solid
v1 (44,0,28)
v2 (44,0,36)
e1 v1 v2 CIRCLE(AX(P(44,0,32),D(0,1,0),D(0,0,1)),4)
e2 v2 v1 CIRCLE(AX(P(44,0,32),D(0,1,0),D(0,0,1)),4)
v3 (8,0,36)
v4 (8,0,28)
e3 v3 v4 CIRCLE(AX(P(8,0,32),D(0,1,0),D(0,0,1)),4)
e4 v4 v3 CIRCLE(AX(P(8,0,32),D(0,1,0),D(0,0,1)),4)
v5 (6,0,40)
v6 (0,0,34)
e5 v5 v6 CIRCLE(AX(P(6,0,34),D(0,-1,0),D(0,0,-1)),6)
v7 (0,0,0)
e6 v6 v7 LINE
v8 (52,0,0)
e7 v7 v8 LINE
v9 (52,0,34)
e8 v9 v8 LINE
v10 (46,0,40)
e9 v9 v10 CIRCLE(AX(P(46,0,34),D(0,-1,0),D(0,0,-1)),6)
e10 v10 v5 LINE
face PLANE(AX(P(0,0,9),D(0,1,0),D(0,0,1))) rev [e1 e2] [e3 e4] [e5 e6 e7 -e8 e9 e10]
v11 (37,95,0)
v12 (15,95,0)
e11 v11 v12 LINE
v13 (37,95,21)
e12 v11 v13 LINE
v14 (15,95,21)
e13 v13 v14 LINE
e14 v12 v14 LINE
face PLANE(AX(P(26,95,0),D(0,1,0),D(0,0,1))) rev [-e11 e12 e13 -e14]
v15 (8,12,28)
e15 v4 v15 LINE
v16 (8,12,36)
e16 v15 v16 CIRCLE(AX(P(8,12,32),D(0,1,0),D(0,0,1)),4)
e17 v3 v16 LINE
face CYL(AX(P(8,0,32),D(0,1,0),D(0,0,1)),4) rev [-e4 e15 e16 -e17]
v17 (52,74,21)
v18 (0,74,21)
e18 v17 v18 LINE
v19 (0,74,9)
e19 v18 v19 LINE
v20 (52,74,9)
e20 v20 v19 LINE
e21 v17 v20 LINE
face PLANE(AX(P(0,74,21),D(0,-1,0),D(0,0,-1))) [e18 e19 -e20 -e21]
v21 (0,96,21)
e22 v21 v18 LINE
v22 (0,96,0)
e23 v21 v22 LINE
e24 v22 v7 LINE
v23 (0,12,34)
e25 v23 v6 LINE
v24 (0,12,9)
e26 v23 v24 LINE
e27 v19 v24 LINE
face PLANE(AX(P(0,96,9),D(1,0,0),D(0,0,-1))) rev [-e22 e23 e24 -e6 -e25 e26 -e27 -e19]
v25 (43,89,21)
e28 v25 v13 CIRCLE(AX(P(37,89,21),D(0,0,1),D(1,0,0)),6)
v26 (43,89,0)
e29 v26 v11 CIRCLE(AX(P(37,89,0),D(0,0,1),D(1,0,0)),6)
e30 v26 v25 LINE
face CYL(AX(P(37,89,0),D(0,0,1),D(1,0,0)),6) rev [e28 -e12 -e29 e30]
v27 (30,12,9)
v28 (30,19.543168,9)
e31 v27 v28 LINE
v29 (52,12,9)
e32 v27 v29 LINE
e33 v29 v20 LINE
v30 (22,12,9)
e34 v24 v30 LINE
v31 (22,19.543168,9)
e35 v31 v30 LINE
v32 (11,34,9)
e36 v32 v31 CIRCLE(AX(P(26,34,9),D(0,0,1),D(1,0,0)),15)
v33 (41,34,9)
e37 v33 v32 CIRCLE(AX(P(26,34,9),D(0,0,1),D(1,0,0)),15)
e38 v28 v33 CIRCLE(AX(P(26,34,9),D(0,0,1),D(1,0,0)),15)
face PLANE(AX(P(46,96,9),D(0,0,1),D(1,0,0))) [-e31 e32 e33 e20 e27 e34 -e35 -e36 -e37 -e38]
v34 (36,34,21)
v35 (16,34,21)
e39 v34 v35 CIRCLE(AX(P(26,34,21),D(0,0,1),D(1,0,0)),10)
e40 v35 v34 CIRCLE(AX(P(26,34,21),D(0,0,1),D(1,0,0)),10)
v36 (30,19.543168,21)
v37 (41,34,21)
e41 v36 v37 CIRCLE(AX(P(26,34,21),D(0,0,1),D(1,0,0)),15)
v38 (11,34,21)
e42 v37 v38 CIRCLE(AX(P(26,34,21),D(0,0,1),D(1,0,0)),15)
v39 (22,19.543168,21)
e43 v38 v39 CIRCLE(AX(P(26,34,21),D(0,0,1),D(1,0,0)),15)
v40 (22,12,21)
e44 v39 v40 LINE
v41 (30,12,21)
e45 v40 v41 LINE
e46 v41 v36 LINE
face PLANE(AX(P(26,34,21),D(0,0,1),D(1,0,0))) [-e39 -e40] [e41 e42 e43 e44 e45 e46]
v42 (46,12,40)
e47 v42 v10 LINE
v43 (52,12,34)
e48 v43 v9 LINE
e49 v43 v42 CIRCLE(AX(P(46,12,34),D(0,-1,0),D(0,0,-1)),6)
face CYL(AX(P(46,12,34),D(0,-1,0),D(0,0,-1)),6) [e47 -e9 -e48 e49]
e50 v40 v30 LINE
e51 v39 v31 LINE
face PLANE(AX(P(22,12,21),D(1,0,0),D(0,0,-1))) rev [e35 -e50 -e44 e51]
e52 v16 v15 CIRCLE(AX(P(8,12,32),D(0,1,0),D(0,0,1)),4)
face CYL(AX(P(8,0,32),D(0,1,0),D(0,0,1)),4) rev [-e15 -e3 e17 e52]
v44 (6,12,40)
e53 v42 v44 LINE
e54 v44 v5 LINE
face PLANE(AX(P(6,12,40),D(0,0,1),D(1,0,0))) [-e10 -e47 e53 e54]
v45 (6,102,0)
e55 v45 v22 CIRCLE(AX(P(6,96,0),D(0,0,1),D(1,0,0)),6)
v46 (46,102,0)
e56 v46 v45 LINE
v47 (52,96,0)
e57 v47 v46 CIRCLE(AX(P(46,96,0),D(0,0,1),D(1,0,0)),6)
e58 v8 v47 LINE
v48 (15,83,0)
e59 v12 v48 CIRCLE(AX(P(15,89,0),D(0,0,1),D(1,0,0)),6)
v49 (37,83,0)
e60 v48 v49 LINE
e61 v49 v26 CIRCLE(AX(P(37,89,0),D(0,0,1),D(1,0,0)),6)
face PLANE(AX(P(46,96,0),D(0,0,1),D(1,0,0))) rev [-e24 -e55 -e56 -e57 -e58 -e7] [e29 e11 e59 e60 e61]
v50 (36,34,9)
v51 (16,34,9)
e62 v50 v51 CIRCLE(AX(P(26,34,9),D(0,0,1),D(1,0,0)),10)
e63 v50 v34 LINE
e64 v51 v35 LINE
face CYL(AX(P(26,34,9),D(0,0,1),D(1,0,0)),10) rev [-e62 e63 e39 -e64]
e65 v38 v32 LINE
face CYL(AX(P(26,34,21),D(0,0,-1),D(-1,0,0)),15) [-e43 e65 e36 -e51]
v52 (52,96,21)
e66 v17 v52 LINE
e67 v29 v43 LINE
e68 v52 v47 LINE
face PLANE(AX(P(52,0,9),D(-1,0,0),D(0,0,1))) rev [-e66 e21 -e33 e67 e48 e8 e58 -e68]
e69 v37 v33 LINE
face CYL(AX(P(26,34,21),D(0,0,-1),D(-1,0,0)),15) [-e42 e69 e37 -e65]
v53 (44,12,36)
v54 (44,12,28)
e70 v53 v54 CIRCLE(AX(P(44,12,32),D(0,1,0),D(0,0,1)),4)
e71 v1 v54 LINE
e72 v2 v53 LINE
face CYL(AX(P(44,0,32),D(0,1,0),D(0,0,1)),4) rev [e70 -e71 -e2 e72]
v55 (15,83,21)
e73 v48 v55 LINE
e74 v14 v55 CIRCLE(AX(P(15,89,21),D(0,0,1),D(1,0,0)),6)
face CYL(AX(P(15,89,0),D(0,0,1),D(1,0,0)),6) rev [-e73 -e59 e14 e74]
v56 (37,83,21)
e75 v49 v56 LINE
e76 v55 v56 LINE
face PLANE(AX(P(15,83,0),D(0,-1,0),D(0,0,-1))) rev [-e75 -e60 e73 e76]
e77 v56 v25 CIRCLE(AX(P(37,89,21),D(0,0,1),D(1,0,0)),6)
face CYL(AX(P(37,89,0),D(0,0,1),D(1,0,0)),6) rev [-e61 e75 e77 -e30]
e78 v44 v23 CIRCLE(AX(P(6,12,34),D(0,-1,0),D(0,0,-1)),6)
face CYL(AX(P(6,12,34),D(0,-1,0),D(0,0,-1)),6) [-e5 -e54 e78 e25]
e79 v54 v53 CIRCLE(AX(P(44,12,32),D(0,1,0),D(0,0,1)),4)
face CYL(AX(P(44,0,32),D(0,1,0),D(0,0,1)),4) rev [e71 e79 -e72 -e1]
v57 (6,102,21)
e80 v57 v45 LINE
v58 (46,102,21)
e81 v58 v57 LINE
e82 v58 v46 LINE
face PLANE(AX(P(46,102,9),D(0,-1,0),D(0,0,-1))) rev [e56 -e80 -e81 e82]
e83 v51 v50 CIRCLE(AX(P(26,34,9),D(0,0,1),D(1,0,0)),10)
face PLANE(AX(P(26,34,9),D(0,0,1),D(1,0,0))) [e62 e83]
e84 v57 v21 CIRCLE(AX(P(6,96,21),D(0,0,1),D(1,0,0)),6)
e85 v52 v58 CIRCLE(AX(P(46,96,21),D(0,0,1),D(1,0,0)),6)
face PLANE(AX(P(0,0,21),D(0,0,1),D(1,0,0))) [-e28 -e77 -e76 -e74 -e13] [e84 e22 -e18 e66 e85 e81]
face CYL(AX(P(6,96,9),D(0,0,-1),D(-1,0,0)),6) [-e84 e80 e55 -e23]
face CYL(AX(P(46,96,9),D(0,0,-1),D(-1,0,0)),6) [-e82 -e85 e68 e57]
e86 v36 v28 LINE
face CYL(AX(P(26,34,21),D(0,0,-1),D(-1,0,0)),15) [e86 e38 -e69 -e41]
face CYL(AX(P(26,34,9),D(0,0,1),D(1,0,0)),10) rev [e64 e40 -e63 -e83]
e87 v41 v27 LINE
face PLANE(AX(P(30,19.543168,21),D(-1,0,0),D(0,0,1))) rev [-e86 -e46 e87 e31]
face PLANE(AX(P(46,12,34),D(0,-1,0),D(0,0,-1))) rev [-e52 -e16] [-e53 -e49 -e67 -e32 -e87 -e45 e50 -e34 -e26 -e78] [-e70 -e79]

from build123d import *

# Parameters (mm, degrees)
BACK_PLATE_DEPTH          = 9
TOP_ARM_DEPTH             = 12
TOP_ARM_SLOT_DEPTH        = 21
BASE_FOOT_DEPTH           = 12
MOUNTING_HOLES_SKETCH_R   = 4
MOUNTING_HOLES_2X_8_DEPTH = 12
BEARING_BOSS_30_DEPTH     = 12
BORE_SKETCH_R             = 10
BORE_20_DEPTH             = 12


with BuildPart() as part:
    # Back Plate Sketch → Back Plate (new body)
    with BuildSketch(Plane.XY):
        with BuildLine():
            Line((0, 0), (52, 0))
            Line((52, 0), (52, 96))
            ThreePointArc((52, 96), (50.242640687, 100.242640687), (46, 102))
            Line((46, 102), (6, 102))
            ThreePointArc((6, 102), (1.757359313, 100.242640687), (0, 96))
            Line((0, 96), (0, 0))
        make_face()
    extrude(amount=BACK_PLATE_DEPTH)

    # Top Arm Sketch → Top Arm (add)
    with BuildSketch(Plane.XY.offset(9)):
        with BuildLine():
            Line((26, 74), (52, 74))
            Line((52, 74), (52, 96))
            ThreePointArc((52, 96), (50.242640687, 100.242640687), (46, 102))
            Line((46, 102), (6, 102))
            ThreePointArc((6, 102), (1.757359313, 100.242640687), (0, 96))
            Line((0, 96), (0, 74))
            Line((0, 74), (26, 74))
        make_face()
    extrude(amount=TOP_ARM_DEPTH)

    # Top Arm Slot Sketch → Top Arm Slot (cut)
    with BuildSketch(Plane.XY.offset(21)):
        with BuildLine():
            Line((26, 95), (15, 95))
            ThreePointArc((15, 95), (9, 89), (15, 83))
            Line((15, 83), (37, 83))
            ThreePointArc((37, 83), (43, 89), (37, 95))
            Line((37, 95), (26, 95))
        make_face()
    extrude(amount=-TOP_ARM_SLOT_DEPTH, mode=Mode.SUBTRACT)

    # Base Foot Sketch → Base Foot (add)
    with BuildSketch(Plane.XZ):
        with BuildLine():
            Line((0, 9), (0, 34))
            ThreePointArc((0, 34), (1.757359313, 38.242640687), (6, 40))
            Line((6, 40), (46, 40))
            ThreePointArc((46, 40), (50.242640687, 38.242640687), (52, 34))
            Line((52, 34), (52, 9))
            Line((52, 9), (52, 0))
            Line((52, 0), (0, 0))
            Line((0, 0), (0, 9))
        make_face()
    extrude(amount=-BASE_FOOT_DEPTH)

    # Mounting Holes Sketch → Mounting Holes 2xØ8 (cut)
    with BuildSketch(Plane(origin=(0, 12, 0), x_dir=(1, 0, 0), z_dir=(0, 1, 0))):
        with Locations(Location((8, -32, 0), (0, 0, 270))):
            Circle(MOUNTING_HOLES_SKETCH_R)
        with Locations(Location((44, -32, 0), (0, 0, 270))):
            Circle(MOUNTING_HOLES_SKETCH_R)
    extrude(amount=-MOUNTING_HOLES_2X_8_DEPTH, mode=Mode.SUBTRACT)

    # Bearing Boss Sketch → Bearing Boss Ø30 (add)
    with BuildSketch(Plane.XY.offset(9)):
        with BuildLine():
            Line((30, 19), (30, 12))
            Line((30, 12), (22, 12))
            Line((22, 12), (22, 19.543167705))
            ThreePointArc((22, 19.543167705), (26, 49), (30, 19.543167705))
            Line((30, 19.543167705), (30, 19))
        make_face()
    extrude(amount=BEARING_BOSS_30_DEPTH)

    # Bore Sketch → Bore Ø20 (cut)
    with BuildSketch(Plane.XY.offset(21)):
        with Locations((26, 34)):
            Circle(BORE_SKETCH_R)
    extrude(amount=-BORE_20_DEPTH, mode=Mode.SUBTRACT)


solid = part.part
